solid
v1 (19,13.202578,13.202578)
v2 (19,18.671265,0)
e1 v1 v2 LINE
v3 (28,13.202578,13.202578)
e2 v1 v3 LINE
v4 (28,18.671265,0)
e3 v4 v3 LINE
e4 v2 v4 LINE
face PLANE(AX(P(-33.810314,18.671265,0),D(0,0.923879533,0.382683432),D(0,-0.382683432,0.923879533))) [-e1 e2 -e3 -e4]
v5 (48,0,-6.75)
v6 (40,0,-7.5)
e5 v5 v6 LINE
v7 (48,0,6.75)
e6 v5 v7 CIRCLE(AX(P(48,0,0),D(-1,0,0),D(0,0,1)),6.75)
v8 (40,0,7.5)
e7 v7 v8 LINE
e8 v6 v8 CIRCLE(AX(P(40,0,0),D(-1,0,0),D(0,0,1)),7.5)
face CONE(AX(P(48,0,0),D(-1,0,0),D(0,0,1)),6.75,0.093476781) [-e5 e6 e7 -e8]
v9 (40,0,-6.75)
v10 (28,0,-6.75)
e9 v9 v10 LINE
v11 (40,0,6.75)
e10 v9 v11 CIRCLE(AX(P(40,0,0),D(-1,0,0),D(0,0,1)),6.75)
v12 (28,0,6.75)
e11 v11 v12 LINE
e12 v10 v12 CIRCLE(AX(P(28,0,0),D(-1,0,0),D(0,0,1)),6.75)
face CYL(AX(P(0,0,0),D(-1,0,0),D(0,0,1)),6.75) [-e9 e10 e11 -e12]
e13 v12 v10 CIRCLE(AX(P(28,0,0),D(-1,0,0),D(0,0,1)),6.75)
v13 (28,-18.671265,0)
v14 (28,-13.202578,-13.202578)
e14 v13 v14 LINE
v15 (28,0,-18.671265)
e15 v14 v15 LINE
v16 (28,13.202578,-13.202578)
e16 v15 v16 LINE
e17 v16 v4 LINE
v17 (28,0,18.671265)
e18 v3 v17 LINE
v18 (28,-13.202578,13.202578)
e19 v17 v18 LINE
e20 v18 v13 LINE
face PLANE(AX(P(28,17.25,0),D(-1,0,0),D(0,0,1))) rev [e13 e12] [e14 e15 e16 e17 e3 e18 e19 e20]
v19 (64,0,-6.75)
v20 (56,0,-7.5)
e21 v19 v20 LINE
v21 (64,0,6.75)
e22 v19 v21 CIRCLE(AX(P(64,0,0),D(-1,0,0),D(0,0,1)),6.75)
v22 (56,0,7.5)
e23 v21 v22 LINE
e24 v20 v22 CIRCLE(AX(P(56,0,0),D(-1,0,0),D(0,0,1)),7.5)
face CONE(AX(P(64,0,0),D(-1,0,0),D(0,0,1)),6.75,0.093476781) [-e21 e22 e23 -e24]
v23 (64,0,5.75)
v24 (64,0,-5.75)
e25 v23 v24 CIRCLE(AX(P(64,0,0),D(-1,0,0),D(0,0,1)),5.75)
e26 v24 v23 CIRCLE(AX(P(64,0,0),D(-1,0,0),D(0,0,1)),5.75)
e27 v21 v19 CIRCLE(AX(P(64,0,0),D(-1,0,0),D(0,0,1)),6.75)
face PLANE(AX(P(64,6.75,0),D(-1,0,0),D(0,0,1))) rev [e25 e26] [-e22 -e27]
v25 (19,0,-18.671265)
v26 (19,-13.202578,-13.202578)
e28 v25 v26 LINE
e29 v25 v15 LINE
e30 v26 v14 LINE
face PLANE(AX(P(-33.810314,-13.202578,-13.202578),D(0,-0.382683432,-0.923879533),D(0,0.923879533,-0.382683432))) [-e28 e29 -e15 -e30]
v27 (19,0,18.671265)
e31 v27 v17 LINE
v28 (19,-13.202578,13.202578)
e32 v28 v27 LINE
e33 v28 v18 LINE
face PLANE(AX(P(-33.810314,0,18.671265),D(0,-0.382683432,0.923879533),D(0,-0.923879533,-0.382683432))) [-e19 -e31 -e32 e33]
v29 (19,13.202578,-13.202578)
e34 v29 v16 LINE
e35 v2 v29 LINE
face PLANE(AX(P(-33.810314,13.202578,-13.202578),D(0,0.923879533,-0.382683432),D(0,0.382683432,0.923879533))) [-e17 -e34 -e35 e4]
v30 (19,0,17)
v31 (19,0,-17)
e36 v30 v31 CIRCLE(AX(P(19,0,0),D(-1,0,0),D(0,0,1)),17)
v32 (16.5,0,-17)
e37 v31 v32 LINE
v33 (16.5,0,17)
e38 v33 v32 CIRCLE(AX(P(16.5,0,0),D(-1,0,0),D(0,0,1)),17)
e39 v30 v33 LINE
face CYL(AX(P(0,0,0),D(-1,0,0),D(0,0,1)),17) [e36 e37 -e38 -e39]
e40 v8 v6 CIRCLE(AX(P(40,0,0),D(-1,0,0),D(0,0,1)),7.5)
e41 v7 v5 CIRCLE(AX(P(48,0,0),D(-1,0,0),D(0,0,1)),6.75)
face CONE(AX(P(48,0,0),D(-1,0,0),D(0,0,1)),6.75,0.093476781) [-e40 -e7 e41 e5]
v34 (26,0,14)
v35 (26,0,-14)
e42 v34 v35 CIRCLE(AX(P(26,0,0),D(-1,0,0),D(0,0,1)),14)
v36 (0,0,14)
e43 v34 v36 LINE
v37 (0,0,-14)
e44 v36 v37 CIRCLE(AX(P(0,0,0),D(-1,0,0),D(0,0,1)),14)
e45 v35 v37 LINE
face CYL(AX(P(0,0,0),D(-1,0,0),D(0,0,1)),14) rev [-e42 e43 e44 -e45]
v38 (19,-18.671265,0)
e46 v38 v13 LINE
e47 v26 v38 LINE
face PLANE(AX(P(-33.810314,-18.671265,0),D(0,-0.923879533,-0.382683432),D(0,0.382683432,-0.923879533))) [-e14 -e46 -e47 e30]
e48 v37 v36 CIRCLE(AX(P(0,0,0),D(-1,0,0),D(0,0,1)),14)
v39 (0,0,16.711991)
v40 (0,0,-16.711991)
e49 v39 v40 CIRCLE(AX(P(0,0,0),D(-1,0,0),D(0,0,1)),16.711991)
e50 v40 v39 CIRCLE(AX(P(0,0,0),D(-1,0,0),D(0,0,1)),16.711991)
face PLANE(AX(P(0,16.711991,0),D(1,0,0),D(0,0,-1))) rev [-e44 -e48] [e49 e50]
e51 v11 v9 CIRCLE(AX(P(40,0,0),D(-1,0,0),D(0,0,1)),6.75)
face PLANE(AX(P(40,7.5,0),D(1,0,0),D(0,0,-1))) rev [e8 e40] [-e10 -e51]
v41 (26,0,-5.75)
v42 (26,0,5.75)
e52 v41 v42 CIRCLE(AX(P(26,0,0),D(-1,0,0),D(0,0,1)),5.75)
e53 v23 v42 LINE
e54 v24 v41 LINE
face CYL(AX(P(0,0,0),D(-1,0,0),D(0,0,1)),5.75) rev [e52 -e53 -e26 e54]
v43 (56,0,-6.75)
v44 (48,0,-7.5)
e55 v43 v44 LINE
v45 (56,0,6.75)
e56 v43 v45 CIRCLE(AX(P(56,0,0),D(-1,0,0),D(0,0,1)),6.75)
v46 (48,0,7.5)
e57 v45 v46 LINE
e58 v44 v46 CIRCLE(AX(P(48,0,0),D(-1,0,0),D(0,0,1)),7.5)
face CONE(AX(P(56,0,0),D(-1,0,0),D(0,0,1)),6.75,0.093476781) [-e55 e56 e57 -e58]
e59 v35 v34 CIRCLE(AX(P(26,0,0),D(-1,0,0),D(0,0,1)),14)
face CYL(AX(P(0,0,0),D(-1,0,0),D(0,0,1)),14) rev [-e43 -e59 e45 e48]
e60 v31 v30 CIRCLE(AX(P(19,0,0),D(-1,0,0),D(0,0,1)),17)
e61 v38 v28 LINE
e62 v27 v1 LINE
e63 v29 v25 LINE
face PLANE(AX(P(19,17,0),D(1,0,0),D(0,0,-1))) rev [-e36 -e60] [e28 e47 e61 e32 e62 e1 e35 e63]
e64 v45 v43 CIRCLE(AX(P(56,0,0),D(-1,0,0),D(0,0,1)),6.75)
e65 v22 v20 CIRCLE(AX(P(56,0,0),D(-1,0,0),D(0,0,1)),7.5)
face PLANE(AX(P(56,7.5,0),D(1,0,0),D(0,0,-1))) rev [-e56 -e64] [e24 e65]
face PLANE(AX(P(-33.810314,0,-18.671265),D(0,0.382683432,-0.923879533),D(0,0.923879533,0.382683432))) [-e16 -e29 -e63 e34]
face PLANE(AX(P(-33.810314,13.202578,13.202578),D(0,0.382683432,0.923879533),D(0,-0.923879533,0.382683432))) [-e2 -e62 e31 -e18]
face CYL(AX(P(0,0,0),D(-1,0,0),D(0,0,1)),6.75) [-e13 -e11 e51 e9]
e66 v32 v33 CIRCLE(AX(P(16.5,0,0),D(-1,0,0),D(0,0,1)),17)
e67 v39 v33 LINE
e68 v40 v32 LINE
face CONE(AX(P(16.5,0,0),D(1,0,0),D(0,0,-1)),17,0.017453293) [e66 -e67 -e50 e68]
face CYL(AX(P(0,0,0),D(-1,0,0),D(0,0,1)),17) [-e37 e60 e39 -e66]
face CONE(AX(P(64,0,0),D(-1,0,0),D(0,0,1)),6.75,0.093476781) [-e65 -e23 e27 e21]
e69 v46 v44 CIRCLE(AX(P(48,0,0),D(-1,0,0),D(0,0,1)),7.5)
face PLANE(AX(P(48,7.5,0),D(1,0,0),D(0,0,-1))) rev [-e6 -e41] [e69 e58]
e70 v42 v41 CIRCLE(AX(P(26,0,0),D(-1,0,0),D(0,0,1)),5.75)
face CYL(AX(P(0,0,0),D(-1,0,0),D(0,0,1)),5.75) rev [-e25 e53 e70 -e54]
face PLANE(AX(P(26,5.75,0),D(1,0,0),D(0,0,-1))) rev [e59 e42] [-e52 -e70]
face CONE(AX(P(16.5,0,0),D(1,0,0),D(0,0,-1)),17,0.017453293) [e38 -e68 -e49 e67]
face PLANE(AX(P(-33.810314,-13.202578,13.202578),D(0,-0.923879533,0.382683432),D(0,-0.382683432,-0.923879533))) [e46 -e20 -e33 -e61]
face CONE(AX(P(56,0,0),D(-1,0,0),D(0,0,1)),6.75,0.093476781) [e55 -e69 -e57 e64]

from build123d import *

# Parameters (mm, degrees)
SKETCH4_R           = 17
BOSS_EXTRUDE1_DEPTH = 9


with BuildPart() as part:
    # Sketch1 → Revolve1 (revolve)
    with BuildSketch(Plane.XY, mode=Mode.PRIVATE) as revolve1_sk:
        Polygon((19, 17), (19, 17.25), (28, 17.25), (28, 6.75), (40, 6.75), (40, 7.5), (48, 6.75), (48, 7.5), (56, 6.75), (56, 7.5), (64, 6.75), (64, 5.75), (26, 5.75), (26, 14), (0, 14), (0, 16.711991429), (16.5, 17), align=None)
    revolve(revolve1_sk.sketch.rotate(Axis((0, 0, 0), (1, 0, 0)), 90), axis=Axis((0, 0, 0), (1, 0, 0)))

    # Sketch4 → Boss-Extrude1 (add)
    with BuildSketch(Plane(origin=(28, 0, 0), x_dir=(0, 0, -1), z_dir=(1, 0, 0))):
        Polygon((0, 18.671265455), (-13.202578417, 13.202578417), (-18.671265455, 0), (-13.202578417, -13.202578417), (0, -18.671265455), (13.202578417, -13.202578417), (18.671265455, 0), (13.202578417, 13.202578417), align=None)
        with Locations(Location((0, 0, 0), (0, 0, 180))):
            Circle(SKETCH4_R, mode=Mode.SUBTRACT)
    extrude(amount=-BOSS_EXTRUDE1_DEPTH)


solid = part.part
